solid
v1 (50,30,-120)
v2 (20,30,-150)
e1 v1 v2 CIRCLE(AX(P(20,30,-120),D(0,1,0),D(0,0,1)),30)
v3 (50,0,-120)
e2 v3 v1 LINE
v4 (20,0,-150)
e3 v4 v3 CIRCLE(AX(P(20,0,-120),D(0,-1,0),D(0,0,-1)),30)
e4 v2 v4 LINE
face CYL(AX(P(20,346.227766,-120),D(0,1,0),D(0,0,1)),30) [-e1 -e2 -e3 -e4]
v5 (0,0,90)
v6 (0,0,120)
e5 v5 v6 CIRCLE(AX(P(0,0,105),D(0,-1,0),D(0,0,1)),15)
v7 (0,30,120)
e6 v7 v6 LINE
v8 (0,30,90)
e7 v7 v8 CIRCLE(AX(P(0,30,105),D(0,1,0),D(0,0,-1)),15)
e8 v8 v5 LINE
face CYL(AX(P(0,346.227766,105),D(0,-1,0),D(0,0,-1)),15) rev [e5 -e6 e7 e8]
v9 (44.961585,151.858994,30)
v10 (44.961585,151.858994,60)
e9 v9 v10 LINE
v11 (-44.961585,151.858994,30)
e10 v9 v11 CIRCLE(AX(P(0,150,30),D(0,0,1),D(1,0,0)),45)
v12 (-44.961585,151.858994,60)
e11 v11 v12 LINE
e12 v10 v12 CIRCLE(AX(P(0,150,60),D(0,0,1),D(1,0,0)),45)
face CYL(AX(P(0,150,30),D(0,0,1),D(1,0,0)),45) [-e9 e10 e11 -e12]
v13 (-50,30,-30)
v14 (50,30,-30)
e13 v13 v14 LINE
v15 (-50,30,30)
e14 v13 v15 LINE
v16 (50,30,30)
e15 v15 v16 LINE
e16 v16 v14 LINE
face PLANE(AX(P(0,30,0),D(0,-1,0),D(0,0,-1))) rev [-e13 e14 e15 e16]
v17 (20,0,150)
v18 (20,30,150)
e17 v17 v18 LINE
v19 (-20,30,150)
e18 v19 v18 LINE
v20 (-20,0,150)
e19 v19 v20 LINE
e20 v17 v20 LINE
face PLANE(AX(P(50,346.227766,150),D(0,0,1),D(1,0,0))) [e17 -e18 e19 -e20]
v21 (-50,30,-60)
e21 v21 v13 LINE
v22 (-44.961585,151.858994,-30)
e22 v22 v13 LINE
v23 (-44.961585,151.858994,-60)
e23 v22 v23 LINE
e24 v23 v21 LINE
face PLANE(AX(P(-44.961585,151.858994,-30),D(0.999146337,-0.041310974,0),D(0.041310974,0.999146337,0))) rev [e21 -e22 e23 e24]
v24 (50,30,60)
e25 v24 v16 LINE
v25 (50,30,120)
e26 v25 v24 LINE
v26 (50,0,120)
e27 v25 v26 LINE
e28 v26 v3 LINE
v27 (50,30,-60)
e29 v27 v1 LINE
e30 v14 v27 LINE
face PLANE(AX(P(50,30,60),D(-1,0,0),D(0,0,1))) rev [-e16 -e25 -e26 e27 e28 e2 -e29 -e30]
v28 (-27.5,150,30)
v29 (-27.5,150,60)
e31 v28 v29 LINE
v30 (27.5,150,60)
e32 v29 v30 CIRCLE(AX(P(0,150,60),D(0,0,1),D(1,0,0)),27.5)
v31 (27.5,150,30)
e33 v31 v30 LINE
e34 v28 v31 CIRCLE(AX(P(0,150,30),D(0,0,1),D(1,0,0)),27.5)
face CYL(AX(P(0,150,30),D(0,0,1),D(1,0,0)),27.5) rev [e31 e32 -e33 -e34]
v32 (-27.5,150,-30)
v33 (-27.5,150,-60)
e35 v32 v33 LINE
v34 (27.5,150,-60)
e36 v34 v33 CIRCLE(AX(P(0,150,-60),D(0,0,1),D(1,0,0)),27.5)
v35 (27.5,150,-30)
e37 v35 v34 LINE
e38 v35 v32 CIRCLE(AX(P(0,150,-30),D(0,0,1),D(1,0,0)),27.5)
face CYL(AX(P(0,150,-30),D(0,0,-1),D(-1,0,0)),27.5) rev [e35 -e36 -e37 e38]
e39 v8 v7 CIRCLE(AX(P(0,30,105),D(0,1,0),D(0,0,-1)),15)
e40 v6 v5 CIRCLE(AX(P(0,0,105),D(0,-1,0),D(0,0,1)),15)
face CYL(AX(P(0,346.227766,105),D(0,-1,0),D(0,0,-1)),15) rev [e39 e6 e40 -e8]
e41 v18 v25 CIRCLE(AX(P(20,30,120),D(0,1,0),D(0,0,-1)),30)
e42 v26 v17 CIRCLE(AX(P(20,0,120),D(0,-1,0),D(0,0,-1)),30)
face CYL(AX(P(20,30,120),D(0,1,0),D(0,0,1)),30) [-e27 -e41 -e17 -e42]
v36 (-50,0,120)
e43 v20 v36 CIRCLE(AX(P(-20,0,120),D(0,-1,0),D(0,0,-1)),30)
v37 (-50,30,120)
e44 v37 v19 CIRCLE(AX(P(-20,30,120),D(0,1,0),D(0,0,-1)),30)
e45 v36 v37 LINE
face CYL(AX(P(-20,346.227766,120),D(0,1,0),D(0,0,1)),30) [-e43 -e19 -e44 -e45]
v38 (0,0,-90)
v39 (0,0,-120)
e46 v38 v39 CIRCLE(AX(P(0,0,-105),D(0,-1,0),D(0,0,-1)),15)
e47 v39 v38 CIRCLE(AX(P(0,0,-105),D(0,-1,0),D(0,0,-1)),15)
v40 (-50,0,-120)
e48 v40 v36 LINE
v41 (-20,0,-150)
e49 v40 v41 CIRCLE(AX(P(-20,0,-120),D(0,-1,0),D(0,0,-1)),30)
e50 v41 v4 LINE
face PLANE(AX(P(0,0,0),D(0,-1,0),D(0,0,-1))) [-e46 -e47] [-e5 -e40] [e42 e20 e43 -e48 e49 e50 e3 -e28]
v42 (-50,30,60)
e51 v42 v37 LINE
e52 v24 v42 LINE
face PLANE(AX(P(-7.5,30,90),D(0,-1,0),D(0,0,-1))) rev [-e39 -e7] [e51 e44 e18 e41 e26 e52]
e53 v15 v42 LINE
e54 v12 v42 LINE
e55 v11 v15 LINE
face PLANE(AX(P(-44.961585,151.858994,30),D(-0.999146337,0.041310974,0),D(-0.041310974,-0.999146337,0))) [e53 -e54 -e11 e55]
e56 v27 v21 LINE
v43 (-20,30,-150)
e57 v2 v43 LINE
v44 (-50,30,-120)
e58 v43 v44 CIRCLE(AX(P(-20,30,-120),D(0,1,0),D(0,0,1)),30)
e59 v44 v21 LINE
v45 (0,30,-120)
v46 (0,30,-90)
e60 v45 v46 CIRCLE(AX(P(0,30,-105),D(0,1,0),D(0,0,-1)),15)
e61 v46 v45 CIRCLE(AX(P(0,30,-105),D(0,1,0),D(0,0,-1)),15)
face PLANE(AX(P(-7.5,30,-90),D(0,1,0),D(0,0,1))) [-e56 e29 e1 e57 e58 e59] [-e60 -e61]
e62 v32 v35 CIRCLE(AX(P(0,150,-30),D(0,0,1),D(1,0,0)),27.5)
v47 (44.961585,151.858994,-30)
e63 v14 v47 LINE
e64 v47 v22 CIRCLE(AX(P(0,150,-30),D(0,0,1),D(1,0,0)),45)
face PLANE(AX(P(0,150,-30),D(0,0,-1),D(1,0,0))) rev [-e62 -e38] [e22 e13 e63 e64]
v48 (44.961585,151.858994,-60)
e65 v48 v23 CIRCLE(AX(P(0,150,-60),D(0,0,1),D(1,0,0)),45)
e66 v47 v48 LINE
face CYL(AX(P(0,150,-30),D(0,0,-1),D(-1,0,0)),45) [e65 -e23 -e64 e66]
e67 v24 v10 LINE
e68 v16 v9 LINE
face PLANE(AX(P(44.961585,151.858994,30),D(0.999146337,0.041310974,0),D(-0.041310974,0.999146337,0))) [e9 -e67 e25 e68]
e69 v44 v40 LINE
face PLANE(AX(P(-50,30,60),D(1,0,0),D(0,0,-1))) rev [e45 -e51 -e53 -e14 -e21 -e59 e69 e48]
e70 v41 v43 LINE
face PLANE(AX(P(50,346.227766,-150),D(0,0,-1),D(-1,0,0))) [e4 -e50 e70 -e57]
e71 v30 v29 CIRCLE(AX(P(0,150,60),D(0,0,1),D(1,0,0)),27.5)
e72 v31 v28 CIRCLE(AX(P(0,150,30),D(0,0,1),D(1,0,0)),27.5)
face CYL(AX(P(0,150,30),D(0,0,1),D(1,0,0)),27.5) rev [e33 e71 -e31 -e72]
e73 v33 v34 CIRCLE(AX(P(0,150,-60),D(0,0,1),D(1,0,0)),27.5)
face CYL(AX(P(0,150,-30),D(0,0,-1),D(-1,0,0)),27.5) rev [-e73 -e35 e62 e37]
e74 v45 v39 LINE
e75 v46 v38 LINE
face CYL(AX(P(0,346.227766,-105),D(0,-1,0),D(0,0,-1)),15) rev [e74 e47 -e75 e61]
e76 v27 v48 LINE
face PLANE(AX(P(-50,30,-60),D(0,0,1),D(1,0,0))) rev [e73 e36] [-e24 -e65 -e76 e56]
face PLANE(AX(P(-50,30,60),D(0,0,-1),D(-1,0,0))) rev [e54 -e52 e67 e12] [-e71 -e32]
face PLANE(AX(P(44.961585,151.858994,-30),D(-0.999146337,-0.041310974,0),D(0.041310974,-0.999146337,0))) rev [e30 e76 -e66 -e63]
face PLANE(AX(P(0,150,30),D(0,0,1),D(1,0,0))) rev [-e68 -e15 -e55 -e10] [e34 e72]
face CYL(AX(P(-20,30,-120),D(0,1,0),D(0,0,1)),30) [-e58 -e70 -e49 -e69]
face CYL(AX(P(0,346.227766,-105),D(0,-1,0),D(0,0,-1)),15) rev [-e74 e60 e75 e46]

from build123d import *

# Parameters (mm, degrees)
SKETCH_1_W           = 100
SKETCH_1_H           = 120
BOSS_EXTRUDE_1_DEPTH = 30
SKETCH_2_R           = 27.5
BOSS_EXTRUDE_2_DEPTH = 30
SKETCH_4_W           = 15
SKETCH_4_H           = 30
BOSS_EXTRUDE_3_DEPTH = 30
SKETCH_5_W           = 100
SKETCH_5_H           = 300
SKETCH_5_R           = 15
BOSS_EXTRUDE_4_DEPTH = 30
FILLET_1_R           = 30


with BuildPart() as part:
    # Sketch 1 → Boss-Extrude 1 (new body)
    with BuildSketch(Plane(origin=(0, 0, 0), x_dir=(1, 0, 0), z_dir=(0, 1, 0))):
        Rectangle(SKETCH_1_W, SKETCH_1_H)
    extrude(amount=BOSS_EXTRUDE_1_DEPTH)

    # Sketch 2 → Boss-Extrude 2 (add)
    with BuildSketch(Plane.XY.offset(60)):
        with BuildLine():
            Line((-44.961585181, 151.858993825), (-50, 30))
            Line((-50, 30), (50, 30))
            Line((50, 30), (44.961585181, 151.858993825))
            ThreePointArc((44.961585181, 151.858993825), (0, 195), (-44.961585181, 151.858993825))
        make_face()
        with Locations((0, 150)):
            Circle(SKETCH_2_R, mode=Mode.SUBTRACT)
    boss_extrude_2 = extrude(amount=-BOSS_EXTRUDE_2_DEPTH)

    # Sketch 4 → Boss-Extrude 3 (add)
    with BuildSketch(Plane.XY.offset(60)):
        with Locations((0, 15)):
            Rectangle(SKETCH_4_W, SKETCH_4_H)
    boss_extrude_3 = extrude(amount=BOSS_EXTRUDE_3_DEPTH)

    # Mirror 1: Boss-Extrude 2, Boss-Extrude 3 across plane
    add(boss_extrude_2.mirror(Plane.XY))
    add(boss_extrude_3.mirror(Plane.XY))

    # Sketch 5 → Boss-Extrude 4 (add)
    with BuildSketch(Plane.XZ):
        Rectangle(SKETCH_5_W, SKETCH_5_H)
        with Locations(Location((0, -105, 0), (0, 0, 270))):
            Circle(SKETCH_5_R, mode=Mode.SUBTRACT)
        with Locations(Location((0, 105, 0), (0, 0, 270))):
            Circle(SKETCH_5_R, mode=Mode.SUBTRACT)
    extrude(amount=-BOSS_EXTRUDE_4_DEPTH)

    # Fillet 1
    fillet_1_edges = [part.edges().sort_by_distance(p)[0] for p in [
        (-50, 15, -150),
        (50, 15, 150),
        (50, 15, -150),
        (-50, 15, 150),
    ]]
    fillet(fillet_1_edges, radius=FILLET_1_R)


solid = part.part
